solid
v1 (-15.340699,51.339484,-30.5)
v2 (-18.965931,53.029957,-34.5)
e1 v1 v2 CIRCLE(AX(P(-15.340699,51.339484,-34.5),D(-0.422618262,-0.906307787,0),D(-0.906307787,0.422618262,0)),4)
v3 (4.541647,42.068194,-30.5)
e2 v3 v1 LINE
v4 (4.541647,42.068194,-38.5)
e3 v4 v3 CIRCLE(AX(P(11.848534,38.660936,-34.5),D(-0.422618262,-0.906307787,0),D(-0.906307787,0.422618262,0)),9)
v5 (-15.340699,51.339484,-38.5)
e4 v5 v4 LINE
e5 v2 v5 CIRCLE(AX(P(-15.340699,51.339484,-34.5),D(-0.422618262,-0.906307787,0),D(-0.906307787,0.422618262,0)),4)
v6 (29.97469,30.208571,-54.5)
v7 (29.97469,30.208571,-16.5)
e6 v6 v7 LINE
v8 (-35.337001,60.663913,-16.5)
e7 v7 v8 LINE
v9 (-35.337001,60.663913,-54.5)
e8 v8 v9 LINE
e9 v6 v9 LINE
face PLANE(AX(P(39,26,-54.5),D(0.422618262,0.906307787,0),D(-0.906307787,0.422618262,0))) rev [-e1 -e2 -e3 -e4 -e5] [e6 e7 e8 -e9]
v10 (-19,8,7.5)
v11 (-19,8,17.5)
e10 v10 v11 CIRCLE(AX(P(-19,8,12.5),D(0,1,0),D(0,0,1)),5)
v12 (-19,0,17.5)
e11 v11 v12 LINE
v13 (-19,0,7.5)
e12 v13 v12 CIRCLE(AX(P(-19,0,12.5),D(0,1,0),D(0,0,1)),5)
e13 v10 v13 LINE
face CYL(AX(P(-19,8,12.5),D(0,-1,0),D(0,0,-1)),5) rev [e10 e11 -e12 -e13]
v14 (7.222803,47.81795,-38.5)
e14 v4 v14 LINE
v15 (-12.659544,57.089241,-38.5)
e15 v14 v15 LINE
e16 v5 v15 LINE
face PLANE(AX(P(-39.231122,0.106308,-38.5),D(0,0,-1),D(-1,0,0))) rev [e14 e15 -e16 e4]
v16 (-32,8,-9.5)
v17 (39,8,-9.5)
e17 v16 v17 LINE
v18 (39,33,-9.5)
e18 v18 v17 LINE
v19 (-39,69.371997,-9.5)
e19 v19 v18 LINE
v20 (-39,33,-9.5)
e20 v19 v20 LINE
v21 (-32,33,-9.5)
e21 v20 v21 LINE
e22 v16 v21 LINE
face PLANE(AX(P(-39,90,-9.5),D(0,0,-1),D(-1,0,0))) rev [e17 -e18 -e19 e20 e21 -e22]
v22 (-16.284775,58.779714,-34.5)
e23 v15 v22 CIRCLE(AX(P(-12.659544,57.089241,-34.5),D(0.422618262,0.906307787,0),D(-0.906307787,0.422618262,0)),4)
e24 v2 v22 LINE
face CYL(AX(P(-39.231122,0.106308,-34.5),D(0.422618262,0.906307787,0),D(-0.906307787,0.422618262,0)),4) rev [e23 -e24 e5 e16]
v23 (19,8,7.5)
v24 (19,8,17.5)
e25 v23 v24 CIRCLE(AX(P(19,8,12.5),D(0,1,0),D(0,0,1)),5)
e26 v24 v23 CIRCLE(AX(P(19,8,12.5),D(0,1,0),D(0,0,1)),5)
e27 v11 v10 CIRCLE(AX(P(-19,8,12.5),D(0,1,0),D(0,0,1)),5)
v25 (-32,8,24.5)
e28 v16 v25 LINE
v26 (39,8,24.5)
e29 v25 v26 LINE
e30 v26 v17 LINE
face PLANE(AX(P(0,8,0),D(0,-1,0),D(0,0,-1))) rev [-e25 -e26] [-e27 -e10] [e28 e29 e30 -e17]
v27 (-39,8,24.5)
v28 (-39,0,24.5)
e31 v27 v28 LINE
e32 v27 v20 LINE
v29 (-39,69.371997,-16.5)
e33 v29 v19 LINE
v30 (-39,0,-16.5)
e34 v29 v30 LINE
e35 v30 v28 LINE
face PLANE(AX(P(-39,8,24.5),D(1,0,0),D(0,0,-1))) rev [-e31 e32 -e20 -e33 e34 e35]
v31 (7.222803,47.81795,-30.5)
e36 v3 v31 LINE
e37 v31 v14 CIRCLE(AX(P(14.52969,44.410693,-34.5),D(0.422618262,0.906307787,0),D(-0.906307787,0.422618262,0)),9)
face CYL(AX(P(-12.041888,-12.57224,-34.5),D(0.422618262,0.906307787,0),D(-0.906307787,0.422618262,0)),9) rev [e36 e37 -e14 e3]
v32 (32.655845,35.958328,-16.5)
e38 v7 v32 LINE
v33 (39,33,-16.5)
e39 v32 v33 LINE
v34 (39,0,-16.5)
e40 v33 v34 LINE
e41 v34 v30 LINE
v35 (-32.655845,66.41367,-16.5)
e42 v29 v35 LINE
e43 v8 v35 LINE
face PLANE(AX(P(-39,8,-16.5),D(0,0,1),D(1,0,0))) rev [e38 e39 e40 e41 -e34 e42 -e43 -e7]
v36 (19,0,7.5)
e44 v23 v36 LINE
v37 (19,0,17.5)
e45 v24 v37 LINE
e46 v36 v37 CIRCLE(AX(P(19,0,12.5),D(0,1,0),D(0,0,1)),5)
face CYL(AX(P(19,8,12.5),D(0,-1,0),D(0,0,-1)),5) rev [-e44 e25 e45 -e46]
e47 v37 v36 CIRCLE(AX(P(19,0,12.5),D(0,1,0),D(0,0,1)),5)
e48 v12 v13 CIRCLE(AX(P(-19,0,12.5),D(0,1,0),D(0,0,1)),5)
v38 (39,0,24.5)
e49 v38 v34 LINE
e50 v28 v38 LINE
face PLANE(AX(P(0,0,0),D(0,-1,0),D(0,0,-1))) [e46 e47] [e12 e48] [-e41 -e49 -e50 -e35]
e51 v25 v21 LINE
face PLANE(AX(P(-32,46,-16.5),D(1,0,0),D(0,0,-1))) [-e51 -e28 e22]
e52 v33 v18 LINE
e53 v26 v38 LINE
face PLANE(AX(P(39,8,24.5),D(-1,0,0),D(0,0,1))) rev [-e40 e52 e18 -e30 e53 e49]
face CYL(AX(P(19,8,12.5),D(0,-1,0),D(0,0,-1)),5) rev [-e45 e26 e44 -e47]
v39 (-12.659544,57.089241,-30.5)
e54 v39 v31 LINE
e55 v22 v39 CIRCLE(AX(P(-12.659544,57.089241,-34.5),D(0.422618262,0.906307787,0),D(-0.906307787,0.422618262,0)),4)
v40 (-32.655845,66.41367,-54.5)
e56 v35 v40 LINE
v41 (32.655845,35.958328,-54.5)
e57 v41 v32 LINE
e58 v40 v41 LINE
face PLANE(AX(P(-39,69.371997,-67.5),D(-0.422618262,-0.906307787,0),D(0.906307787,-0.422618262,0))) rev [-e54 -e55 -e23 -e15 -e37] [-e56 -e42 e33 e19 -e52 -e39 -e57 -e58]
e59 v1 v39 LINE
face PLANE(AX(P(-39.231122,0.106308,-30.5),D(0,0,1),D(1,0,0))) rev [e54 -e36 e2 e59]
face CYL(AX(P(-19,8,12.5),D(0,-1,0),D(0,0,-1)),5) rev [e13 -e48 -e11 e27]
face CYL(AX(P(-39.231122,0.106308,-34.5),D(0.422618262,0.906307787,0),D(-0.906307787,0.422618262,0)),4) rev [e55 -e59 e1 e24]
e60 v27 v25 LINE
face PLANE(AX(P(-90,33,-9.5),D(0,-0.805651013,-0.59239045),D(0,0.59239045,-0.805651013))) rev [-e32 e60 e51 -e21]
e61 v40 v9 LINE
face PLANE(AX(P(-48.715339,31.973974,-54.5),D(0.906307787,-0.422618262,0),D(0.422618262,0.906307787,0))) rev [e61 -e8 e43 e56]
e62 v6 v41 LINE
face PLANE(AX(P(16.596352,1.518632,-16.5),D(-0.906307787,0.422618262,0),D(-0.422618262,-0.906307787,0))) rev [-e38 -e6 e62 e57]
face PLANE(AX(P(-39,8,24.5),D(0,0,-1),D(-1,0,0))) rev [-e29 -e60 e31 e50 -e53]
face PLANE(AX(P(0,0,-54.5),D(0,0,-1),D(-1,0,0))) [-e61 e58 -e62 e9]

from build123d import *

# Parameters (mm, degrees)
BASE_PLATE_SKETCH_W                  = 78
BASE_PLATE_SKETCH_H                  = 41
BASE_PLATE_SKETCH_R                  = 5
BASE_PLATE_WITH_MOUNTING_HOLES_DEPTH = 8
UPRIGHT_WALL_SKETCH_W                = 7
UPRIGHT_WALL_SKETCH_H                = 41
UPRIGHT_WALL_DEPTH                   = 38
BACK_PLATE_SKETCH_W                  = 78
BACK_PLATE_SKETCH_H                  = 7
BACK_PLATE_DEPTH                     = 82
WALL_TRIM_CUT_DEPTH                  = 58
ANGLED_TRIM_CUT_25DEG_DEPTH          = 58
INCLINED_FLANGE_DEPTH                = 38
FLANGE_PROFILE_CUT_SKETCH_W          = 9.958327832
FLANGE_PROFILE_CUT_SKETCH_H          = 38
FLANGE_PROFILE_CUT_SKETCH_W_2        = 7
FLANGE_PROFILE_CUT_DEPTH             = 38
KEYHOLE_SLOT_DIA18_X_W8_REACH        = 92.402


with BuildPart() as part:
    # Base Plate Sketch → Base Plate with Mounting Holes (new body)
    with BuildSketch(Plane(origin=(0, 0, 0), x_dir=(1, 0, 0), z_dir=(0, 1, 0))):
        with Locations((0, -4)):
            Rectangle(BASE_PLATE_SKETCH_W, BASE_PLATE_SKETCH_H)
        with Locations(Location((-19, -12.5, 0), (0, 0, 270))):
            Circle(BASE_PLATE_SKETCH_R, mode=Mode.SUBTRACT)
        with Locations(Location((19, -12.5, 0), (0, 0, 270))):
            Circle(BASE_PLATE_SKETCH_R, mode=Mode.SUBTRACT)
    extrude(amount=BASE_PLATE_WITH_MOUNTING_HOLES_DEPTH)

    # Upright Wall Sketch → Upright Wall (add)
    with BuildSketch(Plane(origin=(0, 8, 0), x_dir=(1, 0, 0), z_dir=(0, 1, 0))):
        with Locations((-35.5, -4)):
            Rectangle(UPRIGHT_WALL_SKETCH_W, UPRIGHT_WALL_SKETCH_H)
    extrude(amount=UPRIGHT_WALL_DEPTH)

    # Back Plate Sketch → Back Plate (add)
    with BuildSketch(Plane(origin=(0, 8, 0), x_dir=(1, 0, 0), z_dir=(0, 1, 0))):
        with Locations((0, 13)):
            Rectangle(BACK_PLATE_SKETCH_W, BACK_PLATE_SKETCH_H)
    extrude(amount=BACK_PLATE_DEPTH)

    # Wall Trim Sketch → Wall Trim Cut (cut)
    with BuildSketch(Plane(origin=(-32, 0, 0), x_dir=(0, 0, -1), z_dir=(1, 0, 0))):
        Polygon((9.5, 33), (-24.5, 8), (-24.5, 46), (9.5, 46), align=None)
    extrude(amount=-WALL_TRIM_CUT_DEPTH, mode=Mode.SUBTRACT)

    # Angled Trim Sketch 25deg → Angled Trim Cut 25deg (cut)
    with BuildSketch(Plane.XY.offset(-9.5)):
        Polygon((-39, 69.371997336), (39, 33), (39, 90), (-39, 90), align=None)
    extrude(amount=-ANGLED_TRIM_CUT_25DEG_DEPTH, mode=Mode.SUBTRACT)

    # Inclined Flange Sketch → Inclined Flange (add)
    with BuildSketch(Plane(origin=(0, 0, -16.5), x_dir=(-1, 0, 0), z_dir=(0, 0, -1))):
        Polygon((-39, 33), (39, 69.371997336), (39, 62.371997336), (-39, 26), align=None)
    extrude(amount=INCLINED_FLANGE_DEPTH)

    # Flange Profile Cut Sketch → Flange Profile Cut (cut)
    with BuildSketch(Plane(origin=(19.605374923, 42.043862201, 0), x_dir=(0.9063077870366495, -0.42261826174070033, 0), z_dir=(0.42261826174070033, 0.9063077870366495, 0))):
        with Locations((19.378764973, 35.5)):
            Rectangle(FLANGE_PROFILE_CUT_SKETCH_W, FLANGE_PROFILE_CUT_SKETCH_H)
        with Locations((-61.163876622, 35.5)):
            Rectangle(FLANGE_PROFILE_CUT_SKETCH_W_2, FLANGE_PROFILE_CUT_SKETCH_H)
    extrude(amount=-FLANGE_PROFILE_CUT_DEPTH, mode=Mode.SUBTRACT)

    # Keyhole Slot Sketch → Keyhole Slot Dia18 x W8 (cut, up to next)
    with BuildSketch(Plane(origin=(19.605374923, 42.043862201, 0), x_dir=(0.9063077870366495, -0.42261826174070033, 0), z_dir=(0.42261826174070033, 0.9063077870366495, 0)), mode=Mode.PRIVATE) as keyhole_slot_dia18_x_w8_sk1:
        with BuildLine():
            Line((-35.600398943, 38.5), (-13.662656691, 38.5))
            ThreePointArc((-13.662656691, 38.5), (3.399601057, 34.5), (-13.662656691, 30.5))
            Line((-13.662656691, 30.5), (-35.600398943, 30.5))
            ThreePointArc((-35.600398943, 30.5), (-39.600398943, 34.5), (-35.600398943, 38.5))
        make_face()
    keyhole_slot_dia18_x_w8_tool1 = extrude(keyhole_slot_dia18_x_w8_sk1.sketch, amount=-KEYHOLE_SLOT_DIA18_X_W8_REACH, mode=Mode.PRIVATE) & part.part
    add(keyhole_slot_dia18_x_w8_tool1.solids().sort_by_distance((6.285215, 48.255155, -34.5))[0], mode=Mode.SUBTRACT)


solid = part.part
